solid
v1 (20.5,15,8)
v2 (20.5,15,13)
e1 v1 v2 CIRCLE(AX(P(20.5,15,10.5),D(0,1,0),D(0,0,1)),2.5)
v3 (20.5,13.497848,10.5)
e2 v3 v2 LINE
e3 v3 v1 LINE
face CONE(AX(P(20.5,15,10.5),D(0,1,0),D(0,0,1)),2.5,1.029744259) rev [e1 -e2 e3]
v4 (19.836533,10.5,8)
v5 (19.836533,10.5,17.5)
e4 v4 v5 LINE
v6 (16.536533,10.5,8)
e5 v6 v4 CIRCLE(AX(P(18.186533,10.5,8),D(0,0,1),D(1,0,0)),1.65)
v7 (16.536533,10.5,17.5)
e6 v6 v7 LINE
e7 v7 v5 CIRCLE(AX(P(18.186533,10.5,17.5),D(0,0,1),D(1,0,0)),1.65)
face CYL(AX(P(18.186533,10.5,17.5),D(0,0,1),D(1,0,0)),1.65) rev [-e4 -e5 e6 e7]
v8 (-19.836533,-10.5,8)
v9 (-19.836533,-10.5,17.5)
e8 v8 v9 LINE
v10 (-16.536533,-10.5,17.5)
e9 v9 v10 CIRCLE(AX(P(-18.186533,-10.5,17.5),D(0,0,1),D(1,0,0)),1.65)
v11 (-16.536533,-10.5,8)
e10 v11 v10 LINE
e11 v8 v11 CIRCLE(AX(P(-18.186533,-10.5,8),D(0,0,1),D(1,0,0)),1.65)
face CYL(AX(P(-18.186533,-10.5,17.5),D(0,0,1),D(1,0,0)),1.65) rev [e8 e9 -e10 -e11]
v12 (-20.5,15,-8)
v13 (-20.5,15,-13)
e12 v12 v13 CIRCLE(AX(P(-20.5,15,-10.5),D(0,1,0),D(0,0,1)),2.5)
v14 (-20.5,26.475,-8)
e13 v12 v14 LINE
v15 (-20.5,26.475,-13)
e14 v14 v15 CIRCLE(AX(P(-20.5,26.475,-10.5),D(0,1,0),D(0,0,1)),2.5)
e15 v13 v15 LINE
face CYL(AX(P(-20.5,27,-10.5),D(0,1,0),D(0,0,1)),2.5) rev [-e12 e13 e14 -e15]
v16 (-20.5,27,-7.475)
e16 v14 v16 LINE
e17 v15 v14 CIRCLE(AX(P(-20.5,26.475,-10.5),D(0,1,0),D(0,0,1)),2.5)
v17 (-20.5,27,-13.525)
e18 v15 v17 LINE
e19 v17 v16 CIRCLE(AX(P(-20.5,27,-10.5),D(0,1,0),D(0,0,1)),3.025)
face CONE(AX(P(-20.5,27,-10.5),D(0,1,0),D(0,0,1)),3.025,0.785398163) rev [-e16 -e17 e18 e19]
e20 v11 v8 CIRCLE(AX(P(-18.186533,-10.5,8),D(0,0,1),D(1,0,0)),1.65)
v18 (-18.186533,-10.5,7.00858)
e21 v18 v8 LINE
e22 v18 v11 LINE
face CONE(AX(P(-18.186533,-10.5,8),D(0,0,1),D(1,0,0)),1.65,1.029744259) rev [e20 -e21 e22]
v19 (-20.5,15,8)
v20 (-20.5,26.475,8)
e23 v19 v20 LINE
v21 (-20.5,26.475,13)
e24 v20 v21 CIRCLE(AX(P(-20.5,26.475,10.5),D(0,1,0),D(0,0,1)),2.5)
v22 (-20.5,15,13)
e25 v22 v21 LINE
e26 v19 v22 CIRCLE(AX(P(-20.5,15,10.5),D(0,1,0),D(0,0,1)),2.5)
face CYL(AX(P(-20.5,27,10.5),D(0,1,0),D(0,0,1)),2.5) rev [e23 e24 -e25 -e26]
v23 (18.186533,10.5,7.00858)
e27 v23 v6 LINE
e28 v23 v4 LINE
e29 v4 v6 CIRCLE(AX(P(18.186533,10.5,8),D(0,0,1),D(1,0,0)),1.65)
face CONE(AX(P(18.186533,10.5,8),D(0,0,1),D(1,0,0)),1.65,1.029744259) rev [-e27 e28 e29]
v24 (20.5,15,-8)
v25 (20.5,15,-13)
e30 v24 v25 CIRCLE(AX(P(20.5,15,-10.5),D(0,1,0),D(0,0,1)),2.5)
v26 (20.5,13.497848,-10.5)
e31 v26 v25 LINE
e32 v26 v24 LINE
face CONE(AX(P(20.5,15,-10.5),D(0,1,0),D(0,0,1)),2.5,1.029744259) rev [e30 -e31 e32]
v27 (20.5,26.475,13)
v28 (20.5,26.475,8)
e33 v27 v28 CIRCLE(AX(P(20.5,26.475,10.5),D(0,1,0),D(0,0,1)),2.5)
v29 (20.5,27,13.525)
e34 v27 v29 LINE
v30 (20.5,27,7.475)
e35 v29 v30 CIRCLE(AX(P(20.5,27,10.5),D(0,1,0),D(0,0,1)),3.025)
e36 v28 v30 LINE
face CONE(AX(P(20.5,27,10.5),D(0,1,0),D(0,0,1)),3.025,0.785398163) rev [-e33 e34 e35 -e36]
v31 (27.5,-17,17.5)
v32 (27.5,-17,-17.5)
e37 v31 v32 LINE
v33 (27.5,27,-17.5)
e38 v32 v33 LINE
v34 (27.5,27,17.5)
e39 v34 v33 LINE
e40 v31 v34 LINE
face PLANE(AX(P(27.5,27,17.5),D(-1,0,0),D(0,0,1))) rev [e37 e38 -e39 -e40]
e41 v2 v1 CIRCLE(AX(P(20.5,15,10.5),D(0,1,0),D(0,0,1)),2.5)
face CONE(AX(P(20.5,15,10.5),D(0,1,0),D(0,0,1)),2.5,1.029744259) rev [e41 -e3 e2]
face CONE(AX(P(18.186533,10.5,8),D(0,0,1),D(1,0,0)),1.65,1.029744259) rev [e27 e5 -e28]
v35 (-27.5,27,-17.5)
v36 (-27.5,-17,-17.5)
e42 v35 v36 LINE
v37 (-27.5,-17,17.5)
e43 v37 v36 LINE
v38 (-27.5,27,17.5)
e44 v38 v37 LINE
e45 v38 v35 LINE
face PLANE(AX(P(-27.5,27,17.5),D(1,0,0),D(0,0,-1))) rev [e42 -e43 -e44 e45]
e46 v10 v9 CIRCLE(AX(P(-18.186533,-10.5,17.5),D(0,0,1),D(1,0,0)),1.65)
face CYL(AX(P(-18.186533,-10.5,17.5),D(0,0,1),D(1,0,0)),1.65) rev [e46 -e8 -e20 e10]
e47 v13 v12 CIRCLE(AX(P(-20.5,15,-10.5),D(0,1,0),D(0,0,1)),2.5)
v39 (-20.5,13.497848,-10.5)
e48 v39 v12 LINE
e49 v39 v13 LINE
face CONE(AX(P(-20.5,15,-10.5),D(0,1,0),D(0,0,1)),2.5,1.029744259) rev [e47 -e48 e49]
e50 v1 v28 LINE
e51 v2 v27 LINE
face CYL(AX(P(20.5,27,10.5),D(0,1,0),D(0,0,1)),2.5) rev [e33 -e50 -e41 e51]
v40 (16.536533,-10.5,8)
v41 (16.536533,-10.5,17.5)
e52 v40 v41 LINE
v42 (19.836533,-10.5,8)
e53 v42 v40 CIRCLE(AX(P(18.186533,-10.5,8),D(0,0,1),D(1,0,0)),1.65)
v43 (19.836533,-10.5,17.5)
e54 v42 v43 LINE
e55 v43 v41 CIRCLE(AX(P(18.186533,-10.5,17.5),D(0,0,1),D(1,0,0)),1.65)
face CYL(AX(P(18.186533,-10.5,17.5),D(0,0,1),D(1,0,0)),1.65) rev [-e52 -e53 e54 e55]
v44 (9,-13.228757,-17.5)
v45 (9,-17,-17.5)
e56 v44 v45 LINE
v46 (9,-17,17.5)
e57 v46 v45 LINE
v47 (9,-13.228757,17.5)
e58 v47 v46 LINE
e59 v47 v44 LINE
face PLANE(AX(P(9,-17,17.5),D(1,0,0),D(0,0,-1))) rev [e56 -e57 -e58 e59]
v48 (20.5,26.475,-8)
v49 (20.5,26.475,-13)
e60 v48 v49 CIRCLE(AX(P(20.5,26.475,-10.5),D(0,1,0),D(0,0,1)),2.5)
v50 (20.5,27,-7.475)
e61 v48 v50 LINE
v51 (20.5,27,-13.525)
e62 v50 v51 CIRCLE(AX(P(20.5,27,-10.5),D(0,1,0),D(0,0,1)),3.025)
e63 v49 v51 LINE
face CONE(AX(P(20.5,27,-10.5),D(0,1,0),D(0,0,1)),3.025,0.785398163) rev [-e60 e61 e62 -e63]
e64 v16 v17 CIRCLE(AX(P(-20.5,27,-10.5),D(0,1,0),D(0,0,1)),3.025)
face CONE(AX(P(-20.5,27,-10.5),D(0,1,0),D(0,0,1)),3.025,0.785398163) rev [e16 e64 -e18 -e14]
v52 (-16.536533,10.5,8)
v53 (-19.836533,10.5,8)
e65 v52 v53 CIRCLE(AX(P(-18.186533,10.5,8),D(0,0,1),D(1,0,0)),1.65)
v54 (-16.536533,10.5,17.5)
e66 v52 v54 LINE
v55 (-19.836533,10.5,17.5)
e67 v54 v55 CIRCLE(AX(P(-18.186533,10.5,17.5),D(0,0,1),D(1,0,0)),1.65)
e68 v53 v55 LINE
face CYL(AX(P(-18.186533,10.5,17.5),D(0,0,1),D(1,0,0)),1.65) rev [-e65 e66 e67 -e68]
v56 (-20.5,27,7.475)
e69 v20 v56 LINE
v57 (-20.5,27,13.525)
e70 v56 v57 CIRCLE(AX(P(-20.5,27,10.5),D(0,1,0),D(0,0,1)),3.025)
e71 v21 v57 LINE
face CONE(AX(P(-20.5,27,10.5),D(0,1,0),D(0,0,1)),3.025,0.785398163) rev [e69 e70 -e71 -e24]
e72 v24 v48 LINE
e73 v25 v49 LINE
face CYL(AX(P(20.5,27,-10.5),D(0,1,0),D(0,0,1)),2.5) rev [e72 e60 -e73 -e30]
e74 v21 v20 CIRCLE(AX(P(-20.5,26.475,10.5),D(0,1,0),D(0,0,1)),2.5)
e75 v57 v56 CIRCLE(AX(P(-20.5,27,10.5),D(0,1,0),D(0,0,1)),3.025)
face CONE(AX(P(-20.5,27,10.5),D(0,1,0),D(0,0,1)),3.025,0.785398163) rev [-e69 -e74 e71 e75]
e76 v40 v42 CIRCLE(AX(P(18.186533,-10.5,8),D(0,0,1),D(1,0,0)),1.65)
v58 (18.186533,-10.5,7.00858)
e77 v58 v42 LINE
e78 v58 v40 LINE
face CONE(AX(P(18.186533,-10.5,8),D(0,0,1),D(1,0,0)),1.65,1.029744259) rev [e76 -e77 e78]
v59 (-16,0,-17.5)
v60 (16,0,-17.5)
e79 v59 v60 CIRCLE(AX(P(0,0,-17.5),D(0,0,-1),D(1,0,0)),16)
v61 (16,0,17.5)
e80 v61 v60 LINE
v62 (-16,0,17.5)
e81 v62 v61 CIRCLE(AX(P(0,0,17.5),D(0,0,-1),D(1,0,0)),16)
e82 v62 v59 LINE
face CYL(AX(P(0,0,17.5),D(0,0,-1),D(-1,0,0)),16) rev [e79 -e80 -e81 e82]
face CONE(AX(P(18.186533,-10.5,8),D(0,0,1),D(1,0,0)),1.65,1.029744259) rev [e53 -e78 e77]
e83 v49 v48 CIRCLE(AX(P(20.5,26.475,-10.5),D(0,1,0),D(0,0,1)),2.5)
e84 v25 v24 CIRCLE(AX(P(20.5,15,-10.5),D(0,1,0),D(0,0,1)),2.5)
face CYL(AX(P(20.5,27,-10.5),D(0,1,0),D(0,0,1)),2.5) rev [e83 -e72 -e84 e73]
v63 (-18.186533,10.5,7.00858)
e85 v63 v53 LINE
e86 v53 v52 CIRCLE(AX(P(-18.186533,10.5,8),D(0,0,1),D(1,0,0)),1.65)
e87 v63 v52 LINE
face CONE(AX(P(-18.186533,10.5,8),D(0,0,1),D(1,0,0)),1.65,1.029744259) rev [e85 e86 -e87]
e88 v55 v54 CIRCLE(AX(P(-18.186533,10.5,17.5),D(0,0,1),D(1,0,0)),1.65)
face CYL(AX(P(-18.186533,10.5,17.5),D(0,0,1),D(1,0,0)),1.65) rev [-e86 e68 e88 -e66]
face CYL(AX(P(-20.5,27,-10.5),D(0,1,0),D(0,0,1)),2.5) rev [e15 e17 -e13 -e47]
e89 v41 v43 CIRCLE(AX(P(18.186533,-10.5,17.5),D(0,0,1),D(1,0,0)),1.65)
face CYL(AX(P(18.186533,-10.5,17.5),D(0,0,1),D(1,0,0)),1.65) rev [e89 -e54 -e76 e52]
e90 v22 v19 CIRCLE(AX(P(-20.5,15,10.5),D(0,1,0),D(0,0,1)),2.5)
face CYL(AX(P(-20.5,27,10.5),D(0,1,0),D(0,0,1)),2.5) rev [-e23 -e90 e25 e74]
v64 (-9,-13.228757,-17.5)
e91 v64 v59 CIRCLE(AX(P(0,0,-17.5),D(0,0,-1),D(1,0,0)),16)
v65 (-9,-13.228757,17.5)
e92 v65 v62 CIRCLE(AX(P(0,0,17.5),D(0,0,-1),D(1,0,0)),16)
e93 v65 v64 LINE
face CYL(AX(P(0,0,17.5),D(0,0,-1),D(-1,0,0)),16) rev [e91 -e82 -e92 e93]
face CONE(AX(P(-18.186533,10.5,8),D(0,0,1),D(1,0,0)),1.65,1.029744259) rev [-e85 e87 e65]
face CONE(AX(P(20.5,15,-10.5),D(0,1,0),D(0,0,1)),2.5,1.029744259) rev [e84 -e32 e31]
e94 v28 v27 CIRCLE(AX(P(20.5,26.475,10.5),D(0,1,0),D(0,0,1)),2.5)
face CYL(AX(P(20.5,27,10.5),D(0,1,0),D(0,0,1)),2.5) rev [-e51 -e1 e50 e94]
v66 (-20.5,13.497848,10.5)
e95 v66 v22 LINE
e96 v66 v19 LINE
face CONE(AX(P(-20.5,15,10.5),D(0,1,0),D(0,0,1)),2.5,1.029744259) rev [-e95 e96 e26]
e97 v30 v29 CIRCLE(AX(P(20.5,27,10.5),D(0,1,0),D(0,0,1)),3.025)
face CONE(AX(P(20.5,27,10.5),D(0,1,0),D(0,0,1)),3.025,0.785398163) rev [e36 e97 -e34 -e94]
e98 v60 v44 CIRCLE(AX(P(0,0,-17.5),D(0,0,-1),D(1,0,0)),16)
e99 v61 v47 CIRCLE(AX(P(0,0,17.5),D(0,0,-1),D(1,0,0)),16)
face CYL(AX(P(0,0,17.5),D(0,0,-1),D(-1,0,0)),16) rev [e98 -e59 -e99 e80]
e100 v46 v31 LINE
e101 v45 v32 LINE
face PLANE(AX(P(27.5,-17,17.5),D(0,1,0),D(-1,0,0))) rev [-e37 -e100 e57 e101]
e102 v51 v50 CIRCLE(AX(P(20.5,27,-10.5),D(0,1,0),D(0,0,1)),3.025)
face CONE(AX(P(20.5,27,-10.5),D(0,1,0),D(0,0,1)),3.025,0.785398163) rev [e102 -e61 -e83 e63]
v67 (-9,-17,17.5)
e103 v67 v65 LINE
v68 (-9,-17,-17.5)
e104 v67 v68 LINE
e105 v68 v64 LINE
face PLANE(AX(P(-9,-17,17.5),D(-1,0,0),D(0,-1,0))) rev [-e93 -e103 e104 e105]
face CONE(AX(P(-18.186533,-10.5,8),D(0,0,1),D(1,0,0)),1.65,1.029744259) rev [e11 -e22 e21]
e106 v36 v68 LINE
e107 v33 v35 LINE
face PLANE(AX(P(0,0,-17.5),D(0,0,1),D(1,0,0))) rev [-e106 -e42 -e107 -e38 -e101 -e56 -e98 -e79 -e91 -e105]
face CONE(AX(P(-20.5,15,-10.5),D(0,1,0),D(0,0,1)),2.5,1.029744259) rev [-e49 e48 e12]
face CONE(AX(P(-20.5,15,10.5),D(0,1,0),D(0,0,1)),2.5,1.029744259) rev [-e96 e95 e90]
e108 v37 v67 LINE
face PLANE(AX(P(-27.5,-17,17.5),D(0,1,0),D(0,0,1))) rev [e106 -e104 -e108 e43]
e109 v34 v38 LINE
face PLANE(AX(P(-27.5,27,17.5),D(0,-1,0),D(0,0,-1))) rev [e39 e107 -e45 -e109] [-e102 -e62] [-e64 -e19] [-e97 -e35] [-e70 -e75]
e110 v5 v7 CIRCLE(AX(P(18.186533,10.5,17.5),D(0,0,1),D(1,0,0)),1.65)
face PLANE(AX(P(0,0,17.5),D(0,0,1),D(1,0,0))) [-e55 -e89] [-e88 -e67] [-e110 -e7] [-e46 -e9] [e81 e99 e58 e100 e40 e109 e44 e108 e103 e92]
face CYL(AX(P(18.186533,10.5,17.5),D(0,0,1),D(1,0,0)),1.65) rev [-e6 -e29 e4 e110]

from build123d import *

# Parameters (mm, degrees)
EXTRUDE_1_DEPTH              = 17.5
HOLE_WIZARD_M4_1_D           = 3.3
HOLE_WIZARD_M4_1_DEPTH       = 9.5
HOLE_WIZARD_M4_1_TIP         = 0.991420021
HOLE_WIZARD_M6_1_D           = 5
HOLE_WIZARD_M6_1_DEPTH       = 12
HOLE_WIZARD_M6_1_CSINK_D     = 6.05
HOLE_WIZARD_M6_1_CSINK_ANGLE = 90
HOLE_WIZARD_M6_1_TIP         = 1.502151548


with BuildPart() as part:
    # 草图1 → 凸台-拉伸1 (new, symmetric)
    with BuildSketch(Plane.XY):
        with BuildLine():
            Line((-27.5, 27), (27.5, 27))
            Line((27.5, 27), (27.5, -17))
            Line((27.5, -17), (9, -17))
            Line((9, -17), (9, -13.228756555))
            ThreePointArc((9, -13.228756555), (0, 16), (-9, -13.228756555))
            Line((-9, -13.228756555), (-9, -17))
            Line((-9, -17), (-27.5, -17))
            Line((-27.5, -17), (-27.5, 27))
        make_face()
    extrude(amount=EXTRUDE_1_DEPTH, both=True)

    # M4 螺纹孔1
    with Locations(Plane.XY.offset(17.5)):
        with Locations((18.186533479, 10.5), (18.186533479, -10.5), (-18.186533479, -10.5), (-18.186533479, 10.5)):
            Hole(HOLE_WIZARD_M4_1_D / 2, depth=HOLE_WIZARD_M4_1_DEPTH)
            with Locations((0, 0, -(HOLE_WIZARD_M4_1_DEPTH + HOLE_WIZARD_M4_1_TIP / 2))):  # 118° drill point
                Cone(0, HOLE_WIZARD_M4_1_D / 2, HOLE_WIZARD_M4_1_TIP, mode=Mode.SUBTRACT)

    # M6 螺纹孔1
    with Locations(Plane(origin=(-20.5, 27, 10.5), x_dir=(0, 0, 1), z_dir=(0, 1, 0))):
        with Locations((0, 0), (-21, 0), (-21, 41), (0, 41)):
            CounterSinkHole(HOLE_WIZARD_M6_1_D / 2, HOLE_WIZARD_M6_1_CSINK_D / 2, depth=HOLE_WIZARD_M6_1_DEPTH, counter_sink_angle=HOLE_WIZARD_M6_1_CSINK_ANGLE)
            with Locations((0, 0, -(HOLE_WIZARD_M6_1_DEPTH + HOLE_WIZARD_M6_1_TIP / 2))):  # 118° drill point
                Cone(0, HOLE_WIZARD_M6_1_D / 2, HOLE_WIZARD_M6_1_TIP, mode=Mode.SUBTRACT)


solid = part.part
